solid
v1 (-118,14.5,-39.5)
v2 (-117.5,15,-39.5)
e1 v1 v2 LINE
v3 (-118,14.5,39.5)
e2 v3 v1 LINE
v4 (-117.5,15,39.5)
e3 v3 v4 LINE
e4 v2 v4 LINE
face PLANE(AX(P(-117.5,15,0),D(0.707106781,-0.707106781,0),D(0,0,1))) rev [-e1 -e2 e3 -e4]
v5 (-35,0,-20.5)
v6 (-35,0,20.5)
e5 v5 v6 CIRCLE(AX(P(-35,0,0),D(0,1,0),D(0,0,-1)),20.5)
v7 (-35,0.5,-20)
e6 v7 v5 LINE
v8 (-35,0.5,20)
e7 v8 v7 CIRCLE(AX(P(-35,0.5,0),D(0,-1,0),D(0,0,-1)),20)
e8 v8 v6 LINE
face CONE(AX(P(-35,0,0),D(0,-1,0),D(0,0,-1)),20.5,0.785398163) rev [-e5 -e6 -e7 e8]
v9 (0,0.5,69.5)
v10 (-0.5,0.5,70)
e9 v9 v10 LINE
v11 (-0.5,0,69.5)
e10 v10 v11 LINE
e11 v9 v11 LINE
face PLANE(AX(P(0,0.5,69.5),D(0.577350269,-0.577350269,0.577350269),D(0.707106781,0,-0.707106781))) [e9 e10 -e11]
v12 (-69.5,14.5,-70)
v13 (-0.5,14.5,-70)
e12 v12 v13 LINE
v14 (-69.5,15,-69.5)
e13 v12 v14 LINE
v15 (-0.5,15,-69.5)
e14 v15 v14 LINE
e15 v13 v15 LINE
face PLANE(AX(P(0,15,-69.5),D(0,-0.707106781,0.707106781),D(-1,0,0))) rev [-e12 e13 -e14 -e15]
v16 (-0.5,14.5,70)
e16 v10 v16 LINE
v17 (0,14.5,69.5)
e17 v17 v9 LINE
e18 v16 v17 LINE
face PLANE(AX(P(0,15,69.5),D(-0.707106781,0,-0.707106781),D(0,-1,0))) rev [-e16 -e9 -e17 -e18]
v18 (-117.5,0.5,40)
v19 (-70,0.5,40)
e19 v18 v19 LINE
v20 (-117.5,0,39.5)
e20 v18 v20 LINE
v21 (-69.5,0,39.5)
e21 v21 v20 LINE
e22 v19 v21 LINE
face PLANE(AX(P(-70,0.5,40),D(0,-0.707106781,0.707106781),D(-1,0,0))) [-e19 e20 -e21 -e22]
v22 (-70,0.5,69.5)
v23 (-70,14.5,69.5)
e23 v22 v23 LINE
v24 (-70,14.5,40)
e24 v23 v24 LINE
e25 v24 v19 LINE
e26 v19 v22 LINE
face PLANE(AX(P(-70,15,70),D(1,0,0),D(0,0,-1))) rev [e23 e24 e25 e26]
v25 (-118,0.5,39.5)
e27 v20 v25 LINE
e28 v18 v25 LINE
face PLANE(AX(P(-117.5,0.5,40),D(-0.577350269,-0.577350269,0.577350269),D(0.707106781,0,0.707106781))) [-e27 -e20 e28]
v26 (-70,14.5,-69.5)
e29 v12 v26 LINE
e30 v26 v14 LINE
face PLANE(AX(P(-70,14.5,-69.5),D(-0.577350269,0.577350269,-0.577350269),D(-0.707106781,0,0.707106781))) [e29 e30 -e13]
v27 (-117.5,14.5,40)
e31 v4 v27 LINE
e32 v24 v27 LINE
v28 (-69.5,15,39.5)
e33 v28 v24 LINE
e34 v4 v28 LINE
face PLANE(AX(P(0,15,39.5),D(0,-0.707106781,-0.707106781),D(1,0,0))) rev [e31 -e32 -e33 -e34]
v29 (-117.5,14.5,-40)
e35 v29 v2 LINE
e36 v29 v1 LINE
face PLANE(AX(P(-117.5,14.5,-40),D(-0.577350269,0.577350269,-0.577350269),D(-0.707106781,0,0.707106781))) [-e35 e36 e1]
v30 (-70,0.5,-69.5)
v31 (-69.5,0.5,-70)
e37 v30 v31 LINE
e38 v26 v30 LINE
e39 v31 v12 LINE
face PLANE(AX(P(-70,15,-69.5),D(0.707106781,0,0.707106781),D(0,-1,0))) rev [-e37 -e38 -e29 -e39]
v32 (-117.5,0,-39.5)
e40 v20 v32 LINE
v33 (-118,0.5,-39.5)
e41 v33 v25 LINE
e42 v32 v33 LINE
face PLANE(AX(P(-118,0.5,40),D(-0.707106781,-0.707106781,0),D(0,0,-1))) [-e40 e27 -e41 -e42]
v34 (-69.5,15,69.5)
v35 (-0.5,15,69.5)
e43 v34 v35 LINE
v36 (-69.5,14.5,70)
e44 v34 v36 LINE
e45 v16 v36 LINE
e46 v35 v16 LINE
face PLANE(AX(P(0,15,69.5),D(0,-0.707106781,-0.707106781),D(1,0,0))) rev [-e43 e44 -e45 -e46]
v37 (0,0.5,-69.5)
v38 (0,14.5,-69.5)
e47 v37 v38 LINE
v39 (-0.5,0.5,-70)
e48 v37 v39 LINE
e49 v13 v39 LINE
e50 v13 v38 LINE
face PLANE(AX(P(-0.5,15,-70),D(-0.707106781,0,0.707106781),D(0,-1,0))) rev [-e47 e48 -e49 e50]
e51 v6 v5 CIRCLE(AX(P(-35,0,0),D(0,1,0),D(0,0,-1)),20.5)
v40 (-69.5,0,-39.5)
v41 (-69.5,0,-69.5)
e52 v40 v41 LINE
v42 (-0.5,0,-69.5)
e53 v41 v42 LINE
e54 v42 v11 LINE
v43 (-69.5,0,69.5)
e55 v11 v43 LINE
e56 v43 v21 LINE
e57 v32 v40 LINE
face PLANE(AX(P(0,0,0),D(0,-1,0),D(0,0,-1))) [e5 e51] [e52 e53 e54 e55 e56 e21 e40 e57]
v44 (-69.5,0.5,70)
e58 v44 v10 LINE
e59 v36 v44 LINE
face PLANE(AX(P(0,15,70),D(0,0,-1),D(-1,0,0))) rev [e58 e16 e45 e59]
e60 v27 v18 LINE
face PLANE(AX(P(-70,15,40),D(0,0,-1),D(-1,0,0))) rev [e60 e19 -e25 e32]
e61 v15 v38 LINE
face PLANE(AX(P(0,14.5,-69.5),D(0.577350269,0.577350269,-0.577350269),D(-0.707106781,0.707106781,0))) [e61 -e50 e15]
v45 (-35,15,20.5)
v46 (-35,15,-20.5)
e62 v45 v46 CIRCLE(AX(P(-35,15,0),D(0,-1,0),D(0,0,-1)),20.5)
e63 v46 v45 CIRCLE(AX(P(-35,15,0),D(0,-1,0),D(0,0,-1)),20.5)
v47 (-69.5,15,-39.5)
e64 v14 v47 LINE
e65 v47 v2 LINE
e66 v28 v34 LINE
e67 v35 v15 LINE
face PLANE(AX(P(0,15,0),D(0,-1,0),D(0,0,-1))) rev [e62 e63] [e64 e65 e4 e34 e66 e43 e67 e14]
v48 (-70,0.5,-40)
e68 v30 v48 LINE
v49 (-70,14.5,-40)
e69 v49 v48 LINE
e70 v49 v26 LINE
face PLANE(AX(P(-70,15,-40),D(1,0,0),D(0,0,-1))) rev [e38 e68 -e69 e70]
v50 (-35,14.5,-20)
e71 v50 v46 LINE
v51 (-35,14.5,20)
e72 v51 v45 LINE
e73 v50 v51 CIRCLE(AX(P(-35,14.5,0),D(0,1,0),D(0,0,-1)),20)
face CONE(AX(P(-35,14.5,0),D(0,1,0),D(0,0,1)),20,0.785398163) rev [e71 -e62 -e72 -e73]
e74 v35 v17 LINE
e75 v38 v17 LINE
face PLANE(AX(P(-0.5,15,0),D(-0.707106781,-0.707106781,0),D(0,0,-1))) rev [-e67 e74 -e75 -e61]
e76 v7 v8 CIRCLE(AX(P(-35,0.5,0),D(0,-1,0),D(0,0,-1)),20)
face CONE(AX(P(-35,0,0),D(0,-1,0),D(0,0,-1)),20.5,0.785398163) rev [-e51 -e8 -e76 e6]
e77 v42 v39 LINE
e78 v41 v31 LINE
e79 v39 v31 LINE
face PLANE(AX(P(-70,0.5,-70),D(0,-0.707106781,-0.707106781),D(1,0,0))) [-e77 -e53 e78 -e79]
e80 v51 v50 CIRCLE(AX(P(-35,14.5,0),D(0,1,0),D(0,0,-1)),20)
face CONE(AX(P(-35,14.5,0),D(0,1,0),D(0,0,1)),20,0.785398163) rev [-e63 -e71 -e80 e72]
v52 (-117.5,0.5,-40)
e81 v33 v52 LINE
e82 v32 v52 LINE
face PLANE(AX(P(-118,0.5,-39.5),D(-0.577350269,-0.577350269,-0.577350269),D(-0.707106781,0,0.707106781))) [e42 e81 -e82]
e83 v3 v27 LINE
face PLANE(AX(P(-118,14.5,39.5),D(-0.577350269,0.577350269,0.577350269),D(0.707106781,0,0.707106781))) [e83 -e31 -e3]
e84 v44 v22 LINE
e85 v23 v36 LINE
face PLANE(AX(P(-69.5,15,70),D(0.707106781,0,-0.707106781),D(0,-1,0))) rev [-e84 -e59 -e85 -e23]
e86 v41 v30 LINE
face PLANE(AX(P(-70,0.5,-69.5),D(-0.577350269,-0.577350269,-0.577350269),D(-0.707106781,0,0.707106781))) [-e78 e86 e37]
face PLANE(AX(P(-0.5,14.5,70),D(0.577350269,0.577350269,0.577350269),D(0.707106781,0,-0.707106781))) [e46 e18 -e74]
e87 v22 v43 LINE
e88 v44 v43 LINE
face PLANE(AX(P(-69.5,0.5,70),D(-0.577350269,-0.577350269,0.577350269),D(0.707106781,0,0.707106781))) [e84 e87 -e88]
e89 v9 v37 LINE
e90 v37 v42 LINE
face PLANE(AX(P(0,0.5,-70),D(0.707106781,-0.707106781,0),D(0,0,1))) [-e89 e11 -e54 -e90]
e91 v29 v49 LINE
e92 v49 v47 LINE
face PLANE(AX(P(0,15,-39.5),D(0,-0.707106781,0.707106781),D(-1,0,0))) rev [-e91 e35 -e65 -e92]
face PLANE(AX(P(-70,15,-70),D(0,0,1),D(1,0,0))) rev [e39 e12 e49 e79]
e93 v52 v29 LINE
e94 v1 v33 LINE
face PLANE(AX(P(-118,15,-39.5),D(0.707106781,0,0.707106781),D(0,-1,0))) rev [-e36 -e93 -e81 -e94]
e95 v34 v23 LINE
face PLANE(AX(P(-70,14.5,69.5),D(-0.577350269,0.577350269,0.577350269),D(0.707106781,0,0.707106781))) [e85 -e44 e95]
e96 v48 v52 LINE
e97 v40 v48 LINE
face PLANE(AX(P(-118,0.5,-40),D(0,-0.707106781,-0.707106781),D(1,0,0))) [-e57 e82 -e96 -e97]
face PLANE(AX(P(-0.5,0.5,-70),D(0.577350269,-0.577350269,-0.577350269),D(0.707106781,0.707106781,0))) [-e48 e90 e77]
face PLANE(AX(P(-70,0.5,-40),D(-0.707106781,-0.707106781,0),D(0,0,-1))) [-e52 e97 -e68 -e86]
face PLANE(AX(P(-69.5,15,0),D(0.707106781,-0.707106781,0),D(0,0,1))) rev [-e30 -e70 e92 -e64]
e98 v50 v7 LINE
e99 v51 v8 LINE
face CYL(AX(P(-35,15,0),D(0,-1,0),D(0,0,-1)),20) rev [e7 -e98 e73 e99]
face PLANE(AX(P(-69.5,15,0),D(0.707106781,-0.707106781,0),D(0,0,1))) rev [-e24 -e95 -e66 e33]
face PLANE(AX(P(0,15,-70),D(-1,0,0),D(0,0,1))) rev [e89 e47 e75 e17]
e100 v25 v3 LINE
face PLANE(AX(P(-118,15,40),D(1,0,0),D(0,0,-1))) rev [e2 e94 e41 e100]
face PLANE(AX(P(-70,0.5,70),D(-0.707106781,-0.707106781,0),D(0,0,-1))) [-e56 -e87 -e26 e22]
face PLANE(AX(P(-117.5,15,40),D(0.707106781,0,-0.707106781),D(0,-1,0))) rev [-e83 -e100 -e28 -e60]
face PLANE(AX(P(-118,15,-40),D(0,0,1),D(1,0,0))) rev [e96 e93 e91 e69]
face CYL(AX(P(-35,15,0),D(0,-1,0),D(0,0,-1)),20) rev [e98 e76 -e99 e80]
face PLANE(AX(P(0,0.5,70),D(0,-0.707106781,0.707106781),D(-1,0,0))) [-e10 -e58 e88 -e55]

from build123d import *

# Parameters (mm, degrees)
SKETCH_1_R      = 20
EXTRUDE_1_DEPTH = 15
CHAMFER_1_SIZE  = 0.5


with BuildPart() as part:
    # 草图1 → 凸台-拉伸1 (new body)
    with BuildSketch(Plane(origin=(0, 0, 0), x_dir=(1, 0, 0), z_dir=(0, 1, 0))):
        Polygon((0, 70), (0, -70), (-70, -70), (-70, -40), (-118, -40), (-118, 40), (-70, 40), (-70, 70), align=None)
        with Locations(Location((-35, 0, 0), (0, 0, 270))):
            Circle(SKETCH_1_R, mode=Mode.SUBTRACT)
    extrude(amount=EXTRUDE_1_DEPTH)

    # 倒角1
    chamfer_1_edges = [part.edges().sort_by_distance(p)[0] for p in [
        (-35, 15, -70),
        (0, 0, 0),
        (-35, 0, 70),
        (-70, 15, -55),
        (-70, 7.5, 70),
        (-118, 7.5, 40),
        (-118, 7.5, -40),
        (-70, 7.5, -70),
        (0, 7.5, -70),
        (0, 7.5, 70),
        (-94, 15, -40),
        (-118, 15, 0),
        (-35, 0, -20),
        (-35, 15, -20),
        (-94, 15, 40),
        (-70, 15, 55),
        (-35, 15, 70),
        (0, 15, 0),
        (-70, 0, 55),
        (-94, 0, 40),
        (-118, 0, 0),
        (-94, 0, -40),
        (-70, 0, -55),
        (-35, 0, -70),
    ]]
    chamfer(chamfer_1_edges, length=CHAMFER_1_SIZE)


solid = part.part
